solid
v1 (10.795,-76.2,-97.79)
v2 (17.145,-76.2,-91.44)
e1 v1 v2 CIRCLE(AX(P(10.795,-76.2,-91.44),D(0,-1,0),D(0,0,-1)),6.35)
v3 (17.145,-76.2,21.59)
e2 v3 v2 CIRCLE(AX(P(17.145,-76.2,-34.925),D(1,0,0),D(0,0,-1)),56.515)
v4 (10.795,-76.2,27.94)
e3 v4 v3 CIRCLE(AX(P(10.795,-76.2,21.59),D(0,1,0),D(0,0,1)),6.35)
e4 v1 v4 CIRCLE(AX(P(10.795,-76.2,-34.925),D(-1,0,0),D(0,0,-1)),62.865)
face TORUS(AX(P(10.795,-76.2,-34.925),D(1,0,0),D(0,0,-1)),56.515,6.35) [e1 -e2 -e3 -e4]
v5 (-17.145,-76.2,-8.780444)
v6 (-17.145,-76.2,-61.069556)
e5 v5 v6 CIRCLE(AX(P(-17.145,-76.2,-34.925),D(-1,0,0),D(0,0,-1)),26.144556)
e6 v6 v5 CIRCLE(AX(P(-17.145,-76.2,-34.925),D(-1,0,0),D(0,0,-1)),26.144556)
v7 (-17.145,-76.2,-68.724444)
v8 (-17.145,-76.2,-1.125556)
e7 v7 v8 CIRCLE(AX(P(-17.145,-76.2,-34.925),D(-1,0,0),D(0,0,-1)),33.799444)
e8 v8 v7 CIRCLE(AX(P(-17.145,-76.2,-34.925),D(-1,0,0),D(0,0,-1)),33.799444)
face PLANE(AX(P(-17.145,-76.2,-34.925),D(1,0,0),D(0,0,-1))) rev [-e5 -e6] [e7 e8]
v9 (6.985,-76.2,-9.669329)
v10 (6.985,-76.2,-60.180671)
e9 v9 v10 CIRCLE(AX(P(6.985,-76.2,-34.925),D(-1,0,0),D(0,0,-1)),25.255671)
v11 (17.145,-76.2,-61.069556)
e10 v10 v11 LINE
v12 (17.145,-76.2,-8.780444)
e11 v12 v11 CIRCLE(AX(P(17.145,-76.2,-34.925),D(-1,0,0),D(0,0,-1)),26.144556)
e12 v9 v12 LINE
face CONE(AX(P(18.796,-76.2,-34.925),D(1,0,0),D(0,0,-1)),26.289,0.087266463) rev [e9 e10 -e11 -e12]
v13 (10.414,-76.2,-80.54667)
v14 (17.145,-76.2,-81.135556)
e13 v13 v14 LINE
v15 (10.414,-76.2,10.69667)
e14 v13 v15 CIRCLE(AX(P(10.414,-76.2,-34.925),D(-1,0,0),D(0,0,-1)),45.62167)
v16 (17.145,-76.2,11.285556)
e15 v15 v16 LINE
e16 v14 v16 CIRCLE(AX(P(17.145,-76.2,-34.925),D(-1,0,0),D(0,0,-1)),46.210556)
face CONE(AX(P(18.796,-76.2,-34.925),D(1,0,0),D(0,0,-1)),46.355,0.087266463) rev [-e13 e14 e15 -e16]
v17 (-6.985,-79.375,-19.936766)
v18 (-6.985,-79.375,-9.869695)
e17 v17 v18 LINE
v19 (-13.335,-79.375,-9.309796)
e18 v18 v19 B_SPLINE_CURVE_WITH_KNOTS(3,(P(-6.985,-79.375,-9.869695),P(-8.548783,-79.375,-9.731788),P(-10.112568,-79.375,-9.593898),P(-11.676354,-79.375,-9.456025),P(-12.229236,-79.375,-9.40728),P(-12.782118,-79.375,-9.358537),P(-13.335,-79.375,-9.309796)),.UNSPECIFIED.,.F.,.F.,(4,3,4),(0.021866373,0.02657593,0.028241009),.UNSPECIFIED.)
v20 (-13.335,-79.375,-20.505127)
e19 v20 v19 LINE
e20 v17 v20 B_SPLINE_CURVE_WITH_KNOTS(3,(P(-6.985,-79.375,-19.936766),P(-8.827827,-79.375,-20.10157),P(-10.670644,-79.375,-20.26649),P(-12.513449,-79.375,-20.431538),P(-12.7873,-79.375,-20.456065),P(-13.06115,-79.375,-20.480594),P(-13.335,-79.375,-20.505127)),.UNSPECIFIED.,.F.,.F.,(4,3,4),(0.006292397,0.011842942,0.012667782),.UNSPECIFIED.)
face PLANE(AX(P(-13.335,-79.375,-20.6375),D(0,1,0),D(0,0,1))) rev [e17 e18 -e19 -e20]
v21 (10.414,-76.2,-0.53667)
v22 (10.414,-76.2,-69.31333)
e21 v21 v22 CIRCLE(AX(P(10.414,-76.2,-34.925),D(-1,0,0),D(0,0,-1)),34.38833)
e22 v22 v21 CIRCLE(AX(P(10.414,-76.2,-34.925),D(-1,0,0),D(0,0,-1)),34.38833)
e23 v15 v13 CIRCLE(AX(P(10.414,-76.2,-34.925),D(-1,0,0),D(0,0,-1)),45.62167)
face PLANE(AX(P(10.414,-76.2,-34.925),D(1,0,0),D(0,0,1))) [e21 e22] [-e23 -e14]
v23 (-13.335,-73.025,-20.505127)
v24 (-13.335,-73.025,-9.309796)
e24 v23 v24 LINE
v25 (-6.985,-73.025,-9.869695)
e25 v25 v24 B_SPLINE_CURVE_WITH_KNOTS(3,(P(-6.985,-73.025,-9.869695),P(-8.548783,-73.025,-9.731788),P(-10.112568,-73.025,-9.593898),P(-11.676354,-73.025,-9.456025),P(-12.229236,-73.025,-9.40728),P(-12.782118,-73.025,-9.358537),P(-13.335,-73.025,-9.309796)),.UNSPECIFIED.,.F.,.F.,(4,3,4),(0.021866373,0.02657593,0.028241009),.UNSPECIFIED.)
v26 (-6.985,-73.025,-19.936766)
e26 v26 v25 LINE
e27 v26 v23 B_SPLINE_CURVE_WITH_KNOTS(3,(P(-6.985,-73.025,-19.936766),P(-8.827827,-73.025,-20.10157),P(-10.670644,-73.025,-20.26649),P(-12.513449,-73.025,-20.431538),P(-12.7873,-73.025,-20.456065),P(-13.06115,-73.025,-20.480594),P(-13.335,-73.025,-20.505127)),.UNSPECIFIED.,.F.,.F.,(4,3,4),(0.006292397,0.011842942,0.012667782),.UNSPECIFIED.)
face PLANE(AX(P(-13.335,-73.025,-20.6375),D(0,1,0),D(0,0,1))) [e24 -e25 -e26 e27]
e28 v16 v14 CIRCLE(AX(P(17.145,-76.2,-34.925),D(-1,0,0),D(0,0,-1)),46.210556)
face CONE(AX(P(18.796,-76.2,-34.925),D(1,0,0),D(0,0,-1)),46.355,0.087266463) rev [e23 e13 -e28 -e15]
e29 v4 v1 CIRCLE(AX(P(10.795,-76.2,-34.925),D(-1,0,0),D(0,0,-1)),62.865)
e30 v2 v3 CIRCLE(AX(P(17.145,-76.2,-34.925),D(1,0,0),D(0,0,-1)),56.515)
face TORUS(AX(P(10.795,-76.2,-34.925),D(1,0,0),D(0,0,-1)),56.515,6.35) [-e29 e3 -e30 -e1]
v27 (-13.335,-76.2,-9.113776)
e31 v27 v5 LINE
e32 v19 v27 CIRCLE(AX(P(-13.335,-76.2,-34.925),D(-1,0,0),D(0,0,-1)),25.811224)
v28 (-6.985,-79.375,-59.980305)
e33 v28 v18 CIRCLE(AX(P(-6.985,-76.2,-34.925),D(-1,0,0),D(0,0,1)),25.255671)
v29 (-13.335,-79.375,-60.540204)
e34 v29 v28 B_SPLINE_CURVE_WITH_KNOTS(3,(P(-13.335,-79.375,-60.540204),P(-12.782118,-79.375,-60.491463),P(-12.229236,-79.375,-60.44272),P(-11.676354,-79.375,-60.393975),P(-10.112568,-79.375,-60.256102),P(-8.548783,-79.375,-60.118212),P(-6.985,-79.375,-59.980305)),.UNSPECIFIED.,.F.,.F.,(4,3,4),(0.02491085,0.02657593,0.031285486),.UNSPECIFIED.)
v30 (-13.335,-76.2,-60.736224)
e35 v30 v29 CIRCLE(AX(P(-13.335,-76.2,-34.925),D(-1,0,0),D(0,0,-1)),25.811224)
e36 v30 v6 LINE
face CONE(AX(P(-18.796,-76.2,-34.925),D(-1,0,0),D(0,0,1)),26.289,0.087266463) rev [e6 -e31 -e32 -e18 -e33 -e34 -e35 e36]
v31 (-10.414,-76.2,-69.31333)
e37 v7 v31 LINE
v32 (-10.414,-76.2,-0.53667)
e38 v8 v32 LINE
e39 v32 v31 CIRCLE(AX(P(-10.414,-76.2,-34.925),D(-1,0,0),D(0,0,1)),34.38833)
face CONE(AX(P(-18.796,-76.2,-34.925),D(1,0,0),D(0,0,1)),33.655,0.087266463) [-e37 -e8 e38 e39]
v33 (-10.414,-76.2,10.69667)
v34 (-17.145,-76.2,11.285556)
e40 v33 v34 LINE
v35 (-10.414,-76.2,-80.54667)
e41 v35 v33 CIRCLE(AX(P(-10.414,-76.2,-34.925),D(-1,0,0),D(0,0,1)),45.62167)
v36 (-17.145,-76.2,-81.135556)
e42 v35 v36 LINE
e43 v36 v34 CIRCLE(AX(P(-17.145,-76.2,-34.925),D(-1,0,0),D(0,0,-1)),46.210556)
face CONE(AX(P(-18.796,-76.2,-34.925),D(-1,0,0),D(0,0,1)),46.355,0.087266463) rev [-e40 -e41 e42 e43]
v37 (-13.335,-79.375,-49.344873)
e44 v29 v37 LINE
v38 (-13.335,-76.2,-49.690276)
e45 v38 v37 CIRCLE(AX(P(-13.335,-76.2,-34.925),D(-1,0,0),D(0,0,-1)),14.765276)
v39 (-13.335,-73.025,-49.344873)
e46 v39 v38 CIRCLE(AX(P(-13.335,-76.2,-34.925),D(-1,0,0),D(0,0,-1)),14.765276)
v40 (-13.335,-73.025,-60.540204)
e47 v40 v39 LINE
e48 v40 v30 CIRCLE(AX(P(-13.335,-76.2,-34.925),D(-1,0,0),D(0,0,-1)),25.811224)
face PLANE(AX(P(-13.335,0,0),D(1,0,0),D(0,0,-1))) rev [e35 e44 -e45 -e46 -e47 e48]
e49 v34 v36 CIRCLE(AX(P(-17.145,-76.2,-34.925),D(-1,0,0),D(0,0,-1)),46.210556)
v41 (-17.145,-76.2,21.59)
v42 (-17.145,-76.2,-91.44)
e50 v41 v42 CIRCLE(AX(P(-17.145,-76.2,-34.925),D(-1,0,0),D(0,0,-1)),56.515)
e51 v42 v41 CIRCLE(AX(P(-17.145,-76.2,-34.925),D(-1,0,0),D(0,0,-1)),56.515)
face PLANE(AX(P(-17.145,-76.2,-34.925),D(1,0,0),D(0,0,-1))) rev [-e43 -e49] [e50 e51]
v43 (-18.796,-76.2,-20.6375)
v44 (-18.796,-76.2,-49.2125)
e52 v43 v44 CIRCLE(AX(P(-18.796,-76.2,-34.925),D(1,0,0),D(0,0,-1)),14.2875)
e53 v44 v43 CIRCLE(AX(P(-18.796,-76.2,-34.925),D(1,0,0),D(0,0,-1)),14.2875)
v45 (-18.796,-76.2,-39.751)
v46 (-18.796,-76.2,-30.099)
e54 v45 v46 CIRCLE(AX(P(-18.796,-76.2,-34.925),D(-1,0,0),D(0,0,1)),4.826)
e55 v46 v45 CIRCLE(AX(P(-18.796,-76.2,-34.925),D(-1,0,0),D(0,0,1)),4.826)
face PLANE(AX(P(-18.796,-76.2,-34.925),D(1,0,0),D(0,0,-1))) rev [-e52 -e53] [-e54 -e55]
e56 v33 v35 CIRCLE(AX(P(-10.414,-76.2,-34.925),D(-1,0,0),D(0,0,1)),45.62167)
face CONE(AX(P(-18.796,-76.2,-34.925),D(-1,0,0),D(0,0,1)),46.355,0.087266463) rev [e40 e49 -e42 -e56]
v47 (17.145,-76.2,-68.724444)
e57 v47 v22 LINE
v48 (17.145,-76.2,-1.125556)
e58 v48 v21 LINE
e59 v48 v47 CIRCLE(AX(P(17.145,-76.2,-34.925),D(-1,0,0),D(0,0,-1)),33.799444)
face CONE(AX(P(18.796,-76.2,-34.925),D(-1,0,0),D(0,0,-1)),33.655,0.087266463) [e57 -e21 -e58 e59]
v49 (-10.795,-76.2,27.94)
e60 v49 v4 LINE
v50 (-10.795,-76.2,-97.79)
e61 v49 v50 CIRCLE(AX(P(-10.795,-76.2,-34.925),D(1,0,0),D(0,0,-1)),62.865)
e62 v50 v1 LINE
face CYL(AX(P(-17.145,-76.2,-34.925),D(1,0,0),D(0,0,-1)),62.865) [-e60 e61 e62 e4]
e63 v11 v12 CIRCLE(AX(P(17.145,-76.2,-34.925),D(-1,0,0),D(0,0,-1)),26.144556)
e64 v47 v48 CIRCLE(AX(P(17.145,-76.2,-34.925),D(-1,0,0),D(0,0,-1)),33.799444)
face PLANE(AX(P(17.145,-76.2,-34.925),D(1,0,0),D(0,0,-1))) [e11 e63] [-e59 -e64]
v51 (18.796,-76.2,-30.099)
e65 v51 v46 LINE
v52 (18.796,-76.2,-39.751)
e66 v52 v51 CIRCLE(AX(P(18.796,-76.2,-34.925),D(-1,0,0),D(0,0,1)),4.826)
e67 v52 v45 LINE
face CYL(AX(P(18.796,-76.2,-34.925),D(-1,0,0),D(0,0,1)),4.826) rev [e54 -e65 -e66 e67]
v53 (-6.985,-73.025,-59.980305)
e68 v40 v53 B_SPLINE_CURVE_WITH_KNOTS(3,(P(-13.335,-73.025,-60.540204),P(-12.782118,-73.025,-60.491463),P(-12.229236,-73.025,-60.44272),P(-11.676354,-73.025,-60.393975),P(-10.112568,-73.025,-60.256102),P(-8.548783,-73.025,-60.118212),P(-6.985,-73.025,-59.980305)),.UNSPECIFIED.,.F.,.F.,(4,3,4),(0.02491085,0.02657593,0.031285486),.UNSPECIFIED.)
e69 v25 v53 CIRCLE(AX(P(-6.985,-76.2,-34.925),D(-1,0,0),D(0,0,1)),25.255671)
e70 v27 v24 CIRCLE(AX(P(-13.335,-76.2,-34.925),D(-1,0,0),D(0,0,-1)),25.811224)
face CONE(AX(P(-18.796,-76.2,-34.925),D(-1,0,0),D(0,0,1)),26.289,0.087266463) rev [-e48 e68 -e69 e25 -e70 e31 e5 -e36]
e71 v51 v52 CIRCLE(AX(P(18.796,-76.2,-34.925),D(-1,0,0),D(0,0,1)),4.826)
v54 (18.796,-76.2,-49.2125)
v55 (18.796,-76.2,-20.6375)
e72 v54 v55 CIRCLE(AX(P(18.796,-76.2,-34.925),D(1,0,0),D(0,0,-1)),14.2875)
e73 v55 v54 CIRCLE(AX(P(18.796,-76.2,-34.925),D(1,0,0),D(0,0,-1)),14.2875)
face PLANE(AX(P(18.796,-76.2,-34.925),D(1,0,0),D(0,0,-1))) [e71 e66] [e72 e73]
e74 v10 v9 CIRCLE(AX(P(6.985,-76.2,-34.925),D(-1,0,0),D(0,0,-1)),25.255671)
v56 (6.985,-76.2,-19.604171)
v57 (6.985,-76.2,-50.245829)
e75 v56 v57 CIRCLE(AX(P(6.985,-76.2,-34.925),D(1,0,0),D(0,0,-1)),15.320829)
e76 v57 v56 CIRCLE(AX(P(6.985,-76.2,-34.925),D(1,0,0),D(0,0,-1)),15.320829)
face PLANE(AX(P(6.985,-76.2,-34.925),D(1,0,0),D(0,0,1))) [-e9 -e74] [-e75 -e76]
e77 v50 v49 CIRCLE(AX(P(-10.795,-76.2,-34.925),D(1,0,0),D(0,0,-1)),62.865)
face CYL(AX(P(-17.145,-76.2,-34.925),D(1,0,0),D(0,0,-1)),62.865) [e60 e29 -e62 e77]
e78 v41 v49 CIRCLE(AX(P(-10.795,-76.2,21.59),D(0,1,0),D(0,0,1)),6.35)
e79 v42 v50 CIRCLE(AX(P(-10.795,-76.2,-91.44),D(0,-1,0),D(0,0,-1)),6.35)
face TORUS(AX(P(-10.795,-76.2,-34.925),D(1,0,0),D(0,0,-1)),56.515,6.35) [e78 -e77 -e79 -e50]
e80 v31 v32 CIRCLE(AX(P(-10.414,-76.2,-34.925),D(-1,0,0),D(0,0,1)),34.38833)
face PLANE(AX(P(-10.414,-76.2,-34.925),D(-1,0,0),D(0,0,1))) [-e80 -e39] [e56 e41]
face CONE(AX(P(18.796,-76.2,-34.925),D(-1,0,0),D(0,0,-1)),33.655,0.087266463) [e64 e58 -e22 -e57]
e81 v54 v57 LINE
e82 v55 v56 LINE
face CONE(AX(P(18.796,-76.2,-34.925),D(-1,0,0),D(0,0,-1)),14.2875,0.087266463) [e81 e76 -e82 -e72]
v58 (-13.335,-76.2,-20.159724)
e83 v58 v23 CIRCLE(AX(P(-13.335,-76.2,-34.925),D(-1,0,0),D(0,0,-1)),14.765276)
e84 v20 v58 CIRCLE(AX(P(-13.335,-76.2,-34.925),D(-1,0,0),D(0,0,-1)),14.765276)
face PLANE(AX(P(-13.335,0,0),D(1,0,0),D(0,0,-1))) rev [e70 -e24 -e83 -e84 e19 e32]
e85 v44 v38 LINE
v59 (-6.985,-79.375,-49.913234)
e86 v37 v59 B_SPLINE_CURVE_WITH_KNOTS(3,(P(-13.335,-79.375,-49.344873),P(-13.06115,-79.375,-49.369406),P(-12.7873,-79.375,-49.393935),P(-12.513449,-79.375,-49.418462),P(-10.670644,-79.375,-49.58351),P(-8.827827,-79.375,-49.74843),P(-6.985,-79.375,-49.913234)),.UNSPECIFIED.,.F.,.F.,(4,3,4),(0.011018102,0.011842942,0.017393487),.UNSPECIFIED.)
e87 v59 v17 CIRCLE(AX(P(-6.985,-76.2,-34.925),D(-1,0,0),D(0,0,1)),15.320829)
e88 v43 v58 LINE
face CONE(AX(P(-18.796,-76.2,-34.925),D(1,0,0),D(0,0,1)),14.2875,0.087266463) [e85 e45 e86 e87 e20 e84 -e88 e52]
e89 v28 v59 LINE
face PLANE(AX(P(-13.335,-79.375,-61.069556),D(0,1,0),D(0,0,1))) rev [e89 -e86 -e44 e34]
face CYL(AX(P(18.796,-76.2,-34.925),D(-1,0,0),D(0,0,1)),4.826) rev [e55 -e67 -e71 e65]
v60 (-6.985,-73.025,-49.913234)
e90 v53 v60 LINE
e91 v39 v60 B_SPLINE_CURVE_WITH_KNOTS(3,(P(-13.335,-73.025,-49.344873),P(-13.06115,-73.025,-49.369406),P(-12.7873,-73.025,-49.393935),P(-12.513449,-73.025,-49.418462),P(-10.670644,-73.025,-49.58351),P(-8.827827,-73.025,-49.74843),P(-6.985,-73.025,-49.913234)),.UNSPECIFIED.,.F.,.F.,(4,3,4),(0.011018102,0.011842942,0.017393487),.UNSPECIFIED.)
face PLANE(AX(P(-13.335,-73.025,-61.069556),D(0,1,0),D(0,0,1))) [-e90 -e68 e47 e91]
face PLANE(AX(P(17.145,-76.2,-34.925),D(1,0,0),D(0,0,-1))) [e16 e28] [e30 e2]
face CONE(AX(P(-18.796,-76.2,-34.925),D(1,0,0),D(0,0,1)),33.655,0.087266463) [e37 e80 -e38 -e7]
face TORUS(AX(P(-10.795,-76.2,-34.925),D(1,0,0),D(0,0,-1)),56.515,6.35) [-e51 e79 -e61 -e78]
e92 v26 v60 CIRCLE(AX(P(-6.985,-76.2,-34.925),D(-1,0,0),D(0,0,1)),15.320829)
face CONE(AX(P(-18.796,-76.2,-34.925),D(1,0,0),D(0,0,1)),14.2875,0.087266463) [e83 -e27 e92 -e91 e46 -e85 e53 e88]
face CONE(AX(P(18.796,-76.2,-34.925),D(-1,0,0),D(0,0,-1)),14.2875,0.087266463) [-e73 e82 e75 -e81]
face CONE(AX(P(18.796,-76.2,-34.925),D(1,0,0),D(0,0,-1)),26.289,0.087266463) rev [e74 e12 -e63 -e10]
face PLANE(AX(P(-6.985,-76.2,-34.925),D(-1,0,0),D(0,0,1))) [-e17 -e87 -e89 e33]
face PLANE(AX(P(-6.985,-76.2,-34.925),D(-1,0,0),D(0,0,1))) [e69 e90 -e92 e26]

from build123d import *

# Parameters (mm, degrees)
BOSS_EXTRUDE1_DEPTH      = 17.145
BOSS_EXTRUDE1_DEPTH_BACK = 17.145
SKETCH1_R                = 62.865
SKETCH2_R                = 46.355
SKETCH2_R_2              = 33.655
CUT_EXTRUDE1_DEPTH       = 6.731
SKETCH3_R                = 26.289
CUT_EXTRUDE2_DEPTH       = 10.16
BOSS_EXTRUDE2_DEPTH      = 18.796
BOSS_EXTRUDE2_DEPTH_BACK = 18.796
SKETCH4_R                = 14.2875
FILLET1_R                = 6.35
DRAFT1_ANGLE             = 5
DRAFT2_ANGLE             = 5
SKETCH5_R                = 4.826
CUT_EXTRUDE3_DEPTH       = 175.112368419
SKETCH6_W                = 11.857056217
SKETCH6_H                = 6.35
EXTRUDE_THIN1_DEPTH      = 6.35


with BuildPart() as part:
    # Sketch1 → Boss-Extrude1 (new, two sides: drawn at the far end of the back side and taken through both)
    with BuildSketch(Plane(origin=(0, 0, 0), x_dir=(0, 0, -1), z_dir=(1, 0, 0)).offset(-BOSS_EXTRUDE1_DEPTH_BACK)):
        with Locations((34.925, -76.2)):
            Circle(SKETCH1_R)
    extrude(amount=BOSS_EXTRUDE1_DEPTH + BOSS_EXTRUDE1_DEPTH_BACK)

    # Sketch2 → Cut-Extrude1 (cut)
    with BuildSketch(Plane.ZY.offset(17.145)):
        with Locations((-34.925, -76.2)):
            Circle(SKETCH2_R)
        with Locations((-34.925, -76.2)):
            Circle(SKETCH2_R_2, mode=Mode.SUBTRACT)
    cut_extrude1 = extrude(amount=-CUT_EXTRUDE1_DEPTH, mode=Mode.SUBTRACT)

    # Sketch3 → Cut-Extrude2 (cut)
    with BuildSketch(Plane.ZY.offset(17.145)):
        with Locations((-34.925, -76.2)):
            Circle(SKETCH3_R)
    cut_extrude2 = extrude(amount=-CUT_EXTRUDE2_DEPTH, mode=Mode.SUBTRACT)

    # Mirror1: Cut-Extrude1, Cut-Extrude2 across plane
    add(cut_extrude1.mirror(Plane(origin=(0, 0, 0), x_dir=(0, 0, 1), z_dir=(1, 0, 0))), mode=Mode.SUBTRACT)
    add(cut_extrude2.mirror(Plane(origin=(0, 0, 0), x_dir=(0, 0, 1), z_dir=(1, 0, 0))), mode=Mode.SUBTRACT)

    # Sketch4 → Boss-Extrude2 (add, two sides: drawn at the far end of the back side and taken through both)
    with BuildSketch(Plane(origin=(0, 0, 0), x_dir=(0, 0, -1), z_dir=(1, 0, 0)).offset(-BOSS_EXTRUDE2_DEPTH_BACK)):
        with Locations((34.925, -76.2)):
            Circle(SKETCH4_R)
    extrude(amount=BOSS_EXTRUDE2_DEPTH + BOSS_EXTRUDE2_DEPTH_BACK)

    # Fillet1
    fillet1_edges = [part.edges().sort_by_distance(p)[0] for p in [
        (-17.145, -76.2, 27.94),
        (17.145, -76.2, 27.94),
    ]]
    fillet(fillet1_edges, radius=FILLET1_R)

    # Draft1
    draft1_faces = [part.faces().sort_by_distance(p)[0] for p in [
        (-13.7795, -76.2, -81.28),
        (-13.7795, -76.2, -68.58),
        (-12.065, -76.2, -61.214),
        (-12.8905, -76.2, -20.6375),
    ]]
    draft(draft1_faces, Plane(origin=(-18.796, -76.2, -34.925), x_dir=(0, 0, -1), z_dir=(-1, 0, 0)), DRAFT1_ANGLE)

    # Draft2
    draft2_faces = [part.faces().sort_by_distance(p)[0] for p in [
        (13.7795, -76.2, -81.28),
        (13.7795, -76.2, -68.58),
        (12.065, -76.2, -61.214),
        (12.8905, -76.2, -20.6375),
    ]]
    draft(draft2_faces, Plane(origin=(18.796, -76.2, -34.925), x_dir=(0, 0, 1), z_dir=(1, 0, 0)), DRAFT2_ANGLE)

    # Sketch5 → Cut-Extrude3 (cut, through all)
    with BuildSketch(Plane.ZY.offset(18.796)):
        with Locations((-34.925, -76.2)):
            Circle(SKETCH5_R)
    extrude(amount=-CUT_EXTRUDE3_DEPTH, mode=Mode.SUBTRACT)

    # Sketch6 → Extrude-Thin1 (add)
    with BuildSketch(Plane.ZY.offset(6.985)):
        with Locations((-55.141028109, -76.2)):
            Rectangle(SKETCH6_W, SKETCH6_H)
        with Locations((-14.708971892, -76.2)):
            Rectangle(SKETCH6_W, SKETCH6_H)
    extrude(amount=EXTRUDE_THIN1_DEPTH)


solid = part.part
